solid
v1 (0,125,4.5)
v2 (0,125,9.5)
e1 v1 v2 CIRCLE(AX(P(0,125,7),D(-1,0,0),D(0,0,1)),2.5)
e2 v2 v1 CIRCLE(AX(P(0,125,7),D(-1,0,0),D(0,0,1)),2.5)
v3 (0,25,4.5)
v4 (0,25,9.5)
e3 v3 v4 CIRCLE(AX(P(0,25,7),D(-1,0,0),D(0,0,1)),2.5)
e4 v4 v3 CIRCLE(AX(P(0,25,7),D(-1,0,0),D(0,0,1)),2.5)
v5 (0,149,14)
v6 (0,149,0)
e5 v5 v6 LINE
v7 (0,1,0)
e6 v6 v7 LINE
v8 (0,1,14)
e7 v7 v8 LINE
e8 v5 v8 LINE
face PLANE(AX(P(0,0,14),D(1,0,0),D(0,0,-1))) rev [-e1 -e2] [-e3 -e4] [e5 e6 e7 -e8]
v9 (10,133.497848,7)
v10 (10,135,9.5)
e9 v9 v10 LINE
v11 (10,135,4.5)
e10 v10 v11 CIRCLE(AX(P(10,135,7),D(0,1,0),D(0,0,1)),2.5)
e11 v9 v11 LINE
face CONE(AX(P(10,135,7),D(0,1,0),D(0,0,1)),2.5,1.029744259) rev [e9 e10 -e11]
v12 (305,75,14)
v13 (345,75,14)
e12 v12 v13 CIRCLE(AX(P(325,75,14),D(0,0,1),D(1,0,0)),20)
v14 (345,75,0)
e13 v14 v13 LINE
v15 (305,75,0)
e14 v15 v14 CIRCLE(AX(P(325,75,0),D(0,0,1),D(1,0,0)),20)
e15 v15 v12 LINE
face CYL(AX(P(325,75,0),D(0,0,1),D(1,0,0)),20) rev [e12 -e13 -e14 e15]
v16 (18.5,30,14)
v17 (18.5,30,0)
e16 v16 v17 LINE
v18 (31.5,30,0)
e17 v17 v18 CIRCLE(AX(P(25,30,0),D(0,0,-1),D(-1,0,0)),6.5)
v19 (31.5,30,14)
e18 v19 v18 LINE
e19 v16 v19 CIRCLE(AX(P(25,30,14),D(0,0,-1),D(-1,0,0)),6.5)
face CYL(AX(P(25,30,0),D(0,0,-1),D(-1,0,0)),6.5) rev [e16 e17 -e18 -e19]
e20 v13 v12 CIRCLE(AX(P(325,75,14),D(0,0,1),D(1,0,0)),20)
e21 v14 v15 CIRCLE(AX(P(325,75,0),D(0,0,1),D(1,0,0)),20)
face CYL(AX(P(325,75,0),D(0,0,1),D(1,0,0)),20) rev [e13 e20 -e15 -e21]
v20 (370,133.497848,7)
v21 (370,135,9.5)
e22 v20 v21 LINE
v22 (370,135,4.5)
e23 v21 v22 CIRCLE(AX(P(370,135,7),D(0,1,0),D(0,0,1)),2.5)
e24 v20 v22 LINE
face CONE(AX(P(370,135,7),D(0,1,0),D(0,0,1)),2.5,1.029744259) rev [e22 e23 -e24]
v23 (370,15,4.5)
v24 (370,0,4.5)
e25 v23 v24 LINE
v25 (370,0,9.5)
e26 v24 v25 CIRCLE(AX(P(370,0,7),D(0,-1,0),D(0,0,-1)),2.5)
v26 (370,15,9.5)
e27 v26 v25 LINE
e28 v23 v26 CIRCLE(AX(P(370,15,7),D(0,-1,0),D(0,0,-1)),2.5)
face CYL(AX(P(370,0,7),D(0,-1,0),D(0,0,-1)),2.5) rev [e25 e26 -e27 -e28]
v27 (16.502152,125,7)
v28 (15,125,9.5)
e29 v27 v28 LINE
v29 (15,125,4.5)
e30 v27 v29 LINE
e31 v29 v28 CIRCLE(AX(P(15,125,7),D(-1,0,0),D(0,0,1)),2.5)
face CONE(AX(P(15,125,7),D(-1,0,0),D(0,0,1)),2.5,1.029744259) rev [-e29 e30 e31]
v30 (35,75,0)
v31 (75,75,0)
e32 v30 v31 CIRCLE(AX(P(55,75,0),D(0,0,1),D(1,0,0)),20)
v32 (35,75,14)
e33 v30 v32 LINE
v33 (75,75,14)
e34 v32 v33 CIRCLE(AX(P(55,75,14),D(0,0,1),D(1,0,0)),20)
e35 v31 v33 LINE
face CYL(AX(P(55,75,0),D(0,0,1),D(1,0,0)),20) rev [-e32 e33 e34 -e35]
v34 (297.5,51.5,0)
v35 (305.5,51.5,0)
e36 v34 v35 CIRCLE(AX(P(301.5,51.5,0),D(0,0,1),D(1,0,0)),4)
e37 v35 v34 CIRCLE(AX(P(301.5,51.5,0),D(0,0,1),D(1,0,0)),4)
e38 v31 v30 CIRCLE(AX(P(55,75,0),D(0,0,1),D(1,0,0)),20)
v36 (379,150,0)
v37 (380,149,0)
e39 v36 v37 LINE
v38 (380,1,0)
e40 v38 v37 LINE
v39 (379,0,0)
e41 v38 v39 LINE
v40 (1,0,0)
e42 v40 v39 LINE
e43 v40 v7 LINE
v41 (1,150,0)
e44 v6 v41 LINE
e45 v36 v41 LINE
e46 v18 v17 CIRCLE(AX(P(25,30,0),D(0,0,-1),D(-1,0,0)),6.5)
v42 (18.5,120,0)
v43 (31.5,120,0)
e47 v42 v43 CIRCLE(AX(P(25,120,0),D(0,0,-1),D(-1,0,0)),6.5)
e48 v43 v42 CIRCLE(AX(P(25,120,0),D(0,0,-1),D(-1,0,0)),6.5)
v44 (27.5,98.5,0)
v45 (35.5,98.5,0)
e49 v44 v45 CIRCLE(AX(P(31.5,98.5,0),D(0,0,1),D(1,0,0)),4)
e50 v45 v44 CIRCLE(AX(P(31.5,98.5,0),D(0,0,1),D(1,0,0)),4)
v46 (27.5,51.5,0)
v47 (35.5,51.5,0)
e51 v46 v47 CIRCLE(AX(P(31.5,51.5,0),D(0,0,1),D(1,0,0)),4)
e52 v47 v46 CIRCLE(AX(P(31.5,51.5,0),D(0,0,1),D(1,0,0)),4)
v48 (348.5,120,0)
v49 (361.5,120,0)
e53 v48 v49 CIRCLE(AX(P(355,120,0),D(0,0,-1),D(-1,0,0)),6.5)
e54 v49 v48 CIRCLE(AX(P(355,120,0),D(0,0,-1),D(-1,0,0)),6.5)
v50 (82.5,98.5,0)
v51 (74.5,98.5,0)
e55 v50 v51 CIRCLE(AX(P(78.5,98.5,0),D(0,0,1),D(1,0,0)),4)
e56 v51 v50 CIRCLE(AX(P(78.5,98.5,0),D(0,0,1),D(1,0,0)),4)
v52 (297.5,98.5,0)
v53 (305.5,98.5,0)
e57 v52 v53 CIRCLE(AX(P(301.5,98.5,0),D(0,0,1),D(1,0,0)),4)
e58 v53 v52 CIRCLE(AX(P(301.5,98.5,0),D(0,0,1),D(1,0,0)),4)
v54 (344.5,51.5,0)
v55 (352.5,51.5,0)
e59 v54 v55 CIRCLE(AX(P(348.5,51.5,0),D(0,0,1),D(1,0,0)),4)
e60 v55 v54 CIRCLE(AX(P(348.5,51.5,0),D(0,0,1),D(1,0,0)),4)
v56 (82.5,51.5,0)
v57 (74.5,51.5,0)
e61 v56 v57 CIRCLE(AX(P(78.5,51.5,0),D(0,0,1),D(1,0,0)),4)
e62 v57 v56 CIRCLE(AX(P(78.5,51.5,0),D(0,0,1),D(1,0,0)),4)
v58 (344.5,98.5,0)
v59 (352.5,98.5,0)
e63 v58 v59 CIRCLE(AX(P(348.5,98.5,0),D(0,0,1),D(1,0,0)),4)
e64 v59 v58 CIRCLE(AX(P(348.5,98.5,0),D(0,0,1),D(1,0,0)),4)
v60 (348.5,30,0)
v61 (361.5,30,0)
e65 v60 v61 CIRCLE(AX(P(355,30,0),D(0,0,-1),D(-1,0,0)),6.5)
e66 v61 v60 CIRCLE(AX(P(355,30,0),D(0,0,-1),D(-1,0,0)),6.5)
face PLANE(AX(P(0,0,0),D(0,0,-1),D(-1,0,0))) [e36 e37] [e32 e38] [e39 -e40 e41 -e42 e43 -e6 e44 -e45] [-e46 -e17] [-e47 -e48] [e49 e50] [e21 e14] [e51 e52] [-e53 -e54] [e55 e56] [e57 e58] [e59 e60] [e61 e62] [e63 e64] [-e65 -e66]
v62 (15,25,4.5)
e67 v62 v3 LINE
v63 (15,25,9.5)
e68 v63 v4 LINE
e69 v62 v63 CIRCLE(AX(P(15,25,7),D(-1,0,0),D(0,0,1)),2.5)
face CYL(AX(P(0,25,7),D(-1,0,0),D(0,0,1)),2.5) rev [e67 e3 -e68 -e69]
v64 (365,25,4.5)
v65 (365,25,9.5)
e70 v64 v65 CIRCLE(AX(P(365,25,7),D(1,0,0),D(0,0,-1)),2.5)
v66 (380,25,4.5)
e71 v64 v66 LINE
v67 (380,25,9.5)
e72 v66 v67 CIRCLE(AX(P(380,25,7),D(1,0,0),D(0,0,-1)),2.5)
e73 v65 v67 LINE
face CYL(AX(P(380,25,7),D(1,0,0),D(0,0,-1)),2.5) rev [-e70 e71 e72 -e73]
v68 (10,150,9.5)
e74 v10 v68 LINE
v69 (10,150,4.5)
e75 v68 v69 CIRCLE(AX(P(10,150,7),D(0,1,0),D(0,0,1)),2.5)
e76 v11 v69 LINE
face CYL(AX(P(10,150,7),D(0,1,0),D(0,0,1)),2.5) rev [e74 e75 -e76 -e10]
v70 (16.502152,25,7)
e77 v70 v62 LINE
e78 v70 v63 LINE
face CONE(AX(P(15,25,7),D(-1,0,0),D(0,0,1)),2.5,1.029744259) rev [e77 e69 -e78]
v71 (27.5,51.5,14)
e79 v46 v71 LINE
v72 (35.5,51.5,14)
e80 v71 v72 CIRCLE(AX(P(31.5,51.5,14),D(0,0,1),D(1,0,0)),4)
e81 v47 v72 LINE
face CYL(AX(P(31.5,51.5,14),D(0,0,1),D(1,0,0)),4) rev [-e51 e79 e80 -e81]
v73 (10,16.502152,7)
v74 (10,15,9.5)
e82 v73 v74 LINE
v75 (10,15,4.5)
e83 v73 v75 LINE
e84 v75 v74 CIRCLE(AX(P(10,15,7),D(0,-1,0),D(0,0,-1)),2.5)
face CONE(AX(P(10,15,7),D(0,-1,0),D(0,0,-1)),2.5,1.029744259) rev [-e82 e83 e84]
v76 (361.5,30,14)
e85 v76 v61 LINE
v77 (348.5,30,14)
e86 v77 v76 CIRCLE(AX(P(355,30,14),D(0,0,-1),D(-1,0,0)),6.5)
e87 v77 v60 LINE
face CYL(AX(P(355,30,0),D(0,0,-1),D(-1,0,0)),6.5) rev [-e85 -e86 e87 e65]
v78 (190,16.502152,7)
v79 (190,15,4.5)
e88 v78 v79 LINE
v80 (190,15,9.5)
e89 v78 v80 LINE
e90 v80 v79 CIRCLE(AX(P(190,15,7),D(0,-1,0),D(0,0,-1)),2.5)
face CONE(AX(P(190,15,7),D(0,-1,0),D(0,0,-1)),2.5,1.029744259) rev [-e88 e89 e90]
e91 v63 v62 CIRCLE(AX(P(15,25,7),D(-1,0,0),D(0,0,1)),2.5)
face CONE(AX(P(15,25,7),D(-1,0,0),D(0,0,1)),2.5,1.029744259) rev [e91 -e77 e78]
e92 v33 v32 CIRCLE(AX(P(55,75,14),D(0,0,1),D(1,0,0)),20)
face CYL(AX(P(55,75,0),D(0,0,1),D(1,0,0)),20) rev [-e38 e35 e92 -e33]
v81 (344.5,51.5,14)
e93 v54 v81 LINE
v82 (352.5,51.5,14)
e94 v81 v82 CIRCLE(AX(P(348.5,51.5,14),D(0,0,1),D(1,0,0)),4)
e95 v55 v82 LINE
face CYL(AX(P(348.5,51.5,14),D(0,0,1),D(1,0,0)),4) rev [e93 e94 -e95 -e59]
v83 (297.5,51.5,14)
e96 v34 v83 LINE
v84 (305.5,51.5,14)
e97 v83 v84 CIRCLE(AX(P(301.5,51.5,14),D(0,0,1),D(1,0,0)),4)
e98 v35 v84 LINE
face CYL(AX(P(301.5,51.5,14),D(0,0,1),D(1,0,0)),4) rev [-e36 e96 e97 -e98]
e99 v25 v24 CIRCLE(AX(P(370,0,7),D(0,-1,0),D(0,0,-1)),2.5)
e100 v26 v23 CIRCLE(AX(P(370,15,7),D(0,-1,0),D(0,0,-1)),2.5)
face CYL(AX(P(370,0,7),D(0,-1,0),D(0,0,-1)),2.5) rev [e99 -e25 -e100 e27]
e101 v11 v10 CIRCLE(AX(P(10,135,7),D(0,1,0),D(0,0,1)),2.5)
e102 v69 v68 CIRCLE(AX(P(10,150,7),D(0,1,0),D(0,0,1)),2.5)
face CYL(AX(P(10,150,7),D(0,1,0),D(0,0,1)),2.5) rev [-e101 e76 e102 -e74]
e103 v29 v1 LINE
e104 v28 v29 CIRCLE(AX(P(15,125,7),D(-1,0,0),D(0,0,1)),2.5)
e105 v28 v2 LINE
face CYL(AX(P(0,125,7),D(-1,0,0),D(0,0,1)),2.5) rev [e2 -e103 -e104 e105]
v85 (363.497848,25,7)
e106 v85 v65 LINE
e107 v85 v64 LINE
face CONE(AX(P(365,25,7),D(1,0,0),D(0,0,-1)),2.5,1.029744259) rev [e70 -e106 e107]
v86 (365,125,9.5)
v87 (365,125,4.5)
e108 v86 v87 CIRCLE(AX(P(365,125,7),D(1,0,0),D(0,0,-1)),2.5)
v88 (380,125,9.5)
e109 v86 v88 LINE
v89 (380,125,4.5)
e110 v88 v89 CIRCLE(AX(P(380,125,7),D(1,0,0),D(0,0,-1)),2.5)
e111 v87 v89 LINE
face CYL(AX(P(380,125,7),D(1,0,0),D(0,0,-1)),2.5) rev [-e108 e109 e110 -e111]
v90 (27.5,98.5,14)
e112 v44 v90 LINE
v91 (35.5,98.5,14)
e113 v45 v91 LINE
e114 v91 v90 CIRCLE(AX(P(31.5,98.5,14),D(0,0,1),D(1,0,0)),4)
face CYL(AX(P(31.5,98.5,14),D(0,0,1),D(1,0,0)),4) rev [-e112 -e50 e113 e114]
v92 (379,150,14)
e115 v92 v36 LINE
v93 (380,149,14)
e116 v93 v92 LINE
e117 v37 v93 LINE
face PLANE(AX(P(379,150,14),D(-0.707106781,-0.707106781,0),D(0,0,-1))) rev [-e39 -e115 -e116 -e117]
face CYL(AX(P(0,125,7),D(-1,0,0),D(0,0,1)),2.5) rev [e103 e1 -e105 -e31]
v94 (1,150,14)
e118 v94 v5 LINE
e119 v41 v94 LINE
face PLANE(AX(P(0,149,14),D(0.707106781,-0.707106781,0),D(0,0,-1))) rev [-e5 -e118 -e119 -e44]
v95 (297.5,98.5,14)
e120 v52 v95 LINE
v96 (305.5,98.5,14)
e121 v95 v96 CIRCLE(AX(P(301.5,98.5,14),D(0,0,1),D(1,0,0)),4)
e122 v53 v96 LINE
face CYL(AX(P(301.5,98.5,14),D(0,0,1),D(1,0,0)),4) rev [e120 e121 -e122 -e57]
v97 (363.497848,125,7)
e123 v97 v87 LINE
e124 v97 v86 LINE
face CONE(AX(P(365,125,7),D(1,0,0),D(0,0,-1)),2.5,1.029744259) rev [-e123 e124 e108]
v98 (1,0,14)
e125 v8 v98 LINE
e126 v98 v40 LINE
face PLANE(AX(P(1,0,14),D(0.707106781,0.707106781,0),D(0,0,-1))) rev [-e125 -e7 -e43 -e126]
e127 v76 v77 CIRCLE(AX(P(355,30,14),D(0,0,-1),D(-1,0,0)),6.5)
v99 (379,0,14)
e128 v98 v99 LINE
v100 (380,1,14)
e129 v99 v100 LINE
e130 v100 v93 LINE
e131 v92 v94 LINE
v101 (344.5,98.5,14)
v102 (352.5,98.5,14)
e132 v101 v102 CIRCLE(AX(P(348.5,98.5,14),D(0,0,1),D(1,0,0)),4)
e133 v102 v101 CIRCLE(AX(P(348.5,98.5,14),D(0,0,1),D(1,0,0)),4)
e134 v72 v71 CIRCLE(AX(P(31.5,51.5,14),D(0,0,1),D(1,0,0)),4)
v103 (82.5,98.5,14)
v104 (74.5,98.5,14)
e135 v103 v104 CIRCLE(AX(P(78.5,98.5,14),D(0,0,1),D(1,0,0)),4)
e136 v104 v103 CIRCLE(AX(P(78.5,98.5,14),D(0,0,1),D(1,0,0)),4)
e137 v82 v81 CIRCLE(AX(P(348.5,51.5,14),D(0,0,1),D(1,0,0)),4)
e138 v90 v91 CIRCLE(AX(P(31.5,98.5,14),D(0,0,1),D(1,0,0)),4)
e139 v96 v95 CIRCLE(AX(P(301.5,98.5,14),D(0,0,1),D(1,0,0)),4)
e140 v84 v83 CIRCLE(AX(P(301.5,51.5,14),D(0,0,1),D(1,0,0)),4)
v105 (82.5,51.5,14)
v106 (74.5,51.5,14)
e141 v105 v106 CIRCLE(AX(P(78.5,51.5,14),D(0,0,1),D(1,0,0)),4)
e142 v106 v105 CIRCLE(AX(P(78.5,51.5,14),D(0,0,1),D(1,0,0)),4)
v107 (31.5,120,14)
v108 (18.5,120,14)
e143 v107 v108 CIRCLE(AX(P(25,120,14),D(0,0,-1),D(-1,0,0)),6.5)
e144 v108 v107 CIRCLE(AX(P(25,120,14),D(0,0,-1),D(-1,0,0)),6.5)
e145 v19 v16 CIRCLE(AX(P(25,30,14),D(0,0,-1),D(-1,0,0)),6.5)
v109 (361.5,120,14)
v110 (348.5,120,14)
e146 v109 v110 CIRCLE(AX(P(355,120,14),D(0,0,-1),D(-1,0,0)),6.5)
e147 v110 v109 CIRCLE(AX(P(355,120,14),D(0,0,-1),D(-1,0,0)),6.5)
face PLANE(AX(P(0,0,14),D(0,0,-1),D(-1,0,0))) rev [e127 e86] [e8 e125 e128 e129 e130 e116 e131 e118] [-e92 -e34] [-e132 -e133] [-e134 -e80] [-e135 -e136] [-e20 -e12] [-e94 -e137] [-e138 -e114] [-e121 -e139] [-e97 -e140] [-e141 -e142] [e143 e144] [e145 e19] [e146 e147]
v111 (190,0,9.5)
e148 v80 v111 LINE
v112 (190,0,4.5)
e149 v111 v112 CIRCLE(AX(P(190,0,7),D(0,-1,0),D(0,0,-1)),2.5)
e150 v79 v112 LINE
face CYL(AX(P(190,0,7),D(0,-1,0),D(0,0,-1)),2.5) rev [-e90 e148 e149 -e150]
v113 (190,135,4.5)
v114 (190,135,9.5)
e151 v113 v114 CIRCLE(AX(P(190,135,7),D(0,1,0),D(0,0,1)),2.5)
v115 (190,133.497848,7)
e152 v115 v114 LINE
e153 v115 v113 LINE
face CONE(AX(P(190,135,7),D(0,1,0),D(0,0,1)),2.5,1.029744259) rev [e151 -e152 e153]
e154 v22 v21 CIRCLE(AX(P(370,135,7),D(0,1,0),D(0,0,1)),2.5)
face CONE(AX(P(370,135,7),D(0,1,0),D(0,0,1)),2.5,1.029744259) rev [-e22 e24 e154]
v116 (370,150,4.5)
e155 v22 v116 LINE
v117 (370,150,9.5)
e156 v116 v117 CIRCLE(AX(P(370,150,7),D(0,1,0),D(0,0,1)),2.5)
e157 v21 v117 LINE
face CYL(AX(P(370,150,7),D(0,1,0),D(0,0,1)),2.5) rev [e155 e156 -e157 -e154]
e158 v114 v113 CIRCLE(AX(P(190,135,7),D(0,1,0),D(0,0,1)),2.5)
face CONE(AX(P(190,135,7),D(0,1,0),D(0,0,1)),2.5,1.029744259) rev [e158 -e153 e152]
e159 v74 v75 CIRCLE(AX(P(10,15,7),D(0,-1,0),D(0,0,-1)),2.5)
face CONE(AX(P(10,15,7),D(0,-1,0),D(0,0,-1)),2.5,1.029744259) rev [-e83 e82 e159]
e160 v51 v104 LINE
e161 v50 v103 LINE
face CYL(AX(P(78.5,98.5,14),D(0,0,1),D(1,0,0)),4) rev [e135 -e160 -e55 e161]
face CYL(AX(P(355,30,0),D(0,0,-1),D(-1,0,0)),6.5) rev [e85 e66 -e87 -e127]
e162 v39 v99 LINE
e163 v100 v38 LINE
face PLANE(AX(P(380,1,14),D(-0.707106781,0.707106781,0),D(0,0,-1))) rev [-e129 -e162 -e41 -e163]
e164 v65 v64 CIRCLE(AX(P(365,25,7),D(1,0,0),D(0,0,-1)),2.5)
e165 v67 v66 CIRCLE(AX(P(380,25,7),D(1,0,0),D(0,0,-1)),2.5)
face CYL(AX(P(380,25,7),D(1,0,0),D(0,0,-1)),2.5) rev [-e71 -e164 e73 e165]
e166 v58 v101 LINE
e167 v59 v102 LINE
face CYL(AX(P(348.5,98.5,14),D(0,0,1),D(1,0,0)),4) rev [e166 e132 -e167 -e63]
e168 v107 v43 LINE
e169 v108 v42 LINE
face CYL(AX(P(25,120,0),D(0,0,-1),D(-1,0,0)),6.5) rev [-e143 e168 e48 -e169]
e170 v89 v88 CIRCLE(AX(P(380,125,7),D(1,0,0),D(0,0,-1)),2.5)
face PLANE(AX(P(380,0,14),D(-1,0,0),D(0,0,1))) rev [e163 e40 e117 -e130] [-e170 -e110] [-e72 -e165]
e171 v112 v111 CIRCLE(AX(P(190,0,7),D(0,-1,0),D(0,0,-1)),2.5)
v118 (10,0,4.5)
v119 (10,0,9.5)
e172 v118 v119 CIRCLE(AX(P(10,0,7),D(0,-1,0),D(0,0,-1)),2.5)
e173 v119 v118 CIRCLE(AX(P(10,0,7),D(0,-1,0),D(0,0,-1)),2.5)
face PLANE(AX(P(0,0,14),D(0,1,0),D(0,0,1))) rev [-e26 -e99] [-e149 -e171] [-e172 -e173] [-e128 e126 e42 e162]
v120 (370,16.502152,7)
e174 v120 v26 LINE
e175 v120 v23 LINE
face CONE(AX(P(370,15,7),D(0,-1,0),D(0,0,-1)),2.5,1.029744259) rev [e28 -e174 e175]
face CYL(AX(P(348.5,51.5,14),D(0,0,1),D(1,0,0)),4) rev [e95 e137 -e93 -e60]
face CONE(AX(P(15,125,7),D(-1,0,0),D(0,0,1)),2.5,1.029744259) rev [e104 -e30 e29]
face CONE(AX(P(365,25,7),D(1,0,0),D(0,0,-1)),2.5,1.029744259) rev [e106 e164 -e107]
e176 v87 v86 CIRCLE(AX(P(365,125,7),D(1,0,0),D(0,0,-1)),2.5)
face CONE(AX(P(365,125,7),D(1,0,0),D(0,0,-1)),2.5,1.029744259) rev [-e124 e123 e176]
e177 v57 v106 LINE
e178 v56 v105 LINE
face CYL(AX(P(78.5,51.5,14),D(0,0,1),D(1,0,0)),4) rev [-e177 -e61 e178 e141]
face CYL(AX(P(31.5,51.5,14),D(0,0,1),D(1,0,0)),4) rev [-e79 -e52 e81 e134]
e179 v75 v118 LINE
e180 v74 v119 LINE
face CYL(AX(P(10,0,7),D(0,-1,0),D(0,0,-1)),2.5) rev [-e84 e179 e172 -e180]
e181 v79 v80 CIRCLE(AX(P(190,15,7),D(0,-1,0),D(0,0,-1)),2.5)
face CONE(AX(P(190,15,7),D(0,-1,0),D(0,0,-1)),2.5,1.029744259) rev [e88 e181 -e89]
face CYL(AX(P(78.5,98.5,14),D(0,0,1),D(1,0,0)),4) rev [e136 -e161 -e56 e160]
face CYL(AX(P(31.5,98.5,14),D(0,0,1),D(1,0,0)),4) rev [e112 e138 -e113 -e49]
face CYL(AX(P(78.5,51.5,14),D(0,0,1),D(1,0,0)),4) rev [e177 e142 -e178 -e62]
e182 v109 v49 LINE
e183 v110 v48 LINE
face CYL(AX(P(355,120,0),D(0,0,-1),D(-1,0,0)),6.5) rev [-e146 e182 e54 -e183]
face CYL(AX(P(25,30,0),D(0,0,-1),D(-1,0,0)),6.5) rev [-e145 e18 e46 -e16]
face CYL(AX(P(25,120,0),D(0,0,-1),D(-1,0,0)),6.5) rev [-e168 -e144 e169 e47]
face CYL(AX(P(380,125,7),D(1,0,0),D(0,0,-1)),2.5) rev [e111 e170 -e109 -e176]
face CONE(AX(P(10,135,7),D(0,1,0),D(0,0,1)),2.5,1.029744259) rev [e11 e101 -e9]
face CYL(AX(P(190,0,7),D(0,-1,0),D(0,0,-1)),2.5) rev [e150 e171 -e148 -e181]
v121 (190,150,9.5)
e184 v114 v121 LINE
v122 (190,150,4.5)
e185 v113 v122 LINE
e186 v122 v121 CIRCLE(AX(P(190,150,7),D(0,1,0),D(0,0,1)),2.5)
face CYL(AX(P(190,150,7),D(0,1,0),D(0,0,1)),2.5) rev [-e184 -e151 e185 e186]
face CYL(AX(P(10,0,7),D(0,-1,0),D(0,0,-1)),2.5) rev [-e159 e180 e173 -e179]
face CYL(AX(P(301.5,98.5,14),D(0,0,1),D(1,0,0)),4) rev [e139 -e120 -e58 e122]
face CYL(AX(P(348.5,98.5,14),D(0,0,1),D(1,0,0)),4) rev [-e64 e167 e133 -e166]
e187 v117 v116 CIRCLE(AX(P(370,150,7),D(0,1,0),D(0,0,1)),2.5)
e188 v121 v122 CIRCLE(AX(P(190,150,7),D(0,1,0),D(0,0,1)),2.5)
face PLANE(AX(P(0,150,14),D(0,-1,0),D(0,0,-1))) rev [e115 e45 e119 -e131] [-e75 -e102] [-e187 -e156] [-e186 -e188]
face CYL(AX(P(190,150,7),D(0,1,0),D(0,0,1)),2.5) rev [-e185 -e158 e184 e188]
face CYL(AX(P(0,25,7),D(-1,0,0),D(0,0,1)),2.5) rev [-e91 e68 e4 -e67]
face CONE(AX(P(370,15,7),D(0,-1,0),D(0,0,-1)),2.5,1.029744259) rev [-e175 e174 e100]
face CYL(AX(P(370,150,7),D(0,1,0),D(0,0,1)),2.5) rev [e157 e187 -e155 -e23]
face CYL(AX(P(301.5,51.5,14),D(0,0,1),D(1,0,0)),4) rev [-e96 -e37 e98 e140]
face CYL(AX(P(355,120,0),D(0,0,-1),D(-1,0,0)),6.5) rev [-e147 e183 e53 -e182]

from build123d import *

# Parameters (mm, degrees)
SKETCH1_W                  = 380
SKETCH1_H                  = 150
BOSS_EXTRUDE1_DEPTH        = 14
CHAMFER1_SIZE              = 1
SKETCH2_R                  = 20
CUT_EXTRUDE1_DEPTH         = 409.773776067
F_8_0_8_DIAMETER_HOLE1_D   = 8
LPATTERN1_COUNT            = 2
LPATTERN1_PITCH            = 270
F_13_0_13_DIAMETER_HOLE1_D = 13
M6_TAPPED_HOLE1_D          = 5
M6_TAPPED_HOLE1_DEPTH      = 15
M6_TAPPED_HOLE1_TIP        = 1.502151548
M6_TAPPED_HOLE2_D          = 5
M6_TAPPED_HOLE2_DEPTH      = 15
M6_TAPPED_HOLE2_TIP        = 1.502151548
M6_TAPPED_HOLE3_D          = 5
M6_TAPPED_HOLE3_DEPTH      = 15
M6_TAPPED_HOLE3_TIP        = 1.502151548
M6_TAPPED_HOLE4_D          = 5
M6_TAPPED_HOLE4_DEPTH      = 15
M6_TAPPED_HOLE4_TIP        = 1.502151548


with BuildPart() as part:
    # Sketch1 → Boss-Extrude1 (new body)
    with BuildSketch(Plane.XY):
        with Locations((190, 75)):
            Rectangle(SKETCH1_W, SKETCH1_H)
    extrude(amount=BOSS_EXTRUDE1_DEPTH)

    # Chamfer1
    chamfer1_edges = [part.edges().sort_by_distance(p)[0] for p in [
        (0, 150, 7),
        (380, 150, 7),
        (380, 0, 7),
        (0, 0, 7),
    ]]
    chamfer(chamfer1_edges, length=CHAMFER1_SIZE)

    # Sketch2 → Cut-Extrude1 (cut, through all)
    with BuildSketch(Plane.XY.offset(14)):
        with Locations((55, 75)):
            Circle(SKETCH2_R)
        with Locations((325, 75)):
            Circle(SKETCH2_R)
    extrude(amount=-CUT_EXTRUDE1_DEPTH, mode=Mode.SUBTRACT)

    # Ø8.0 (8) Diameter Hole1 (through all)
    with Locations(Plane(origin=(31.5, 98.5, 14), x_dir=(1, 0, 0), z_dir=(0, 0, 1))):
        with Locations((0, 0), (47, 0), (47, -47), (0, -47)):
            f_8_0_8_diameter_hole1 = Hole(F_8_0_8_DIAMETER_HOLE1_D / 2)

    # LPattern1: Ø8.0 (8) Diameter Hole1 ×2
    with Locations(*[(i * LPATTERN1_PITCH, 0, 0) for i in range(1, LPATTERN1_COUNT)]):
        add(f_8_0_8_diameter_hole1, mode=Mode.SUBTRACT)

    # Ø13.0 (13) Diameter Hole1 (through all)
    with Locations(Plane(origin=(355, 120, 0), x_dir=(-1, 0, 0), z_dir=(0, 0, -1))):
        with Locations((0, 0), (0, -90), (330, -90), (330, 0)):
            Hole(F_13_0_13_DIAMETER_HOLE1_D / 2)

    # M6 Tapped Hole1
    with Locations(Plane(origin=(0, 0, 0), x_dir=(-1, 0, 0), z_dir=(0, -1, 0))):
        with Locations((-370, -7), (-190, -7), (-10, -7)):
            Hole(M6_TAPPED_HOLE1_D / 2, depth=M6_TAPPED_HOLE1_DEPTH)
            with Locations((0, 0, -(M6_TAPPED_HOLE1_DEPTH + M6_TAPPED_HOLE1_TIP / 2))):  # 118° drill point
                Cone(0, M6_TAPPED_HOLE1_D / 2, M6_TAPPED_HOLE1_TIP, mode=Mode.SUBTRACT)

    # M6 Tapped Hole2
    with Locations(Plane(origin=(0, 150, 0), x_dir=(1, 0, 0), z_dir=(0, 1, 0))):
        with Locations((370, -7), (190, -7), (10, -7)):
            Hole(M6_TAPPED_HOLE2_D / 2, depth=M6_TAPPED_HOLE2_DEPTH)
            with Locations((0, 0, -(M6_TAPPED_HOLE2_DEPTH + M6_TAPPED_HOLE2_TIP / 2))):  # 118° drill point
                Cone(0, M6_TAPPED_HOLE2_D / 2, M6_TAPPED_HOLE2_TIP, mode=Mode.SUBTRACT)

    # M6 Tapped Hole3
    with Locations(Plane(origin=(380, 0, 0), x_dir=(0, 0, -1), z_dir=(1, 0, 0))):
        with Locations((-7, 125), (-7, 25)):
            Hole(M6_TAPPED_HOLE3_D / 2, depth=M6_TAPPED_HOLE3_DEPTH)
            with Locations((0, 0, -(M6_TAPPED_HOLE3_DEPTH + M6_TAPPED_HOLE3_TIP / 2))):  # 118° drill point
                Cone(0, M6_TAPPED_HOLE3_D / 2, M6_TAPPED_HOLE3_TIP, mode=Mode.SUBTRACT)

    # M6 Tapped Hole4
    with Locations(Plane.ZY):
        with Locations((7, 25), (7, 125)):
            Hole(M6_TAPPED_HOLE4_D / 2, depth=M6_TAPPED_HOLE4_DEPTH)
            with Locations((0, 0, -(M6_TAPPED_HOLE4_DEPTH + M6_TAPPED_HOLE4_TIP / 2))):  # 118° drill point
                Cone(0, M6_TAPPED_HOLE4_D / 2, M6_TAPPED_HOLE4_TIP, mode=Mode.SUBTRACT)


solid = part.part
